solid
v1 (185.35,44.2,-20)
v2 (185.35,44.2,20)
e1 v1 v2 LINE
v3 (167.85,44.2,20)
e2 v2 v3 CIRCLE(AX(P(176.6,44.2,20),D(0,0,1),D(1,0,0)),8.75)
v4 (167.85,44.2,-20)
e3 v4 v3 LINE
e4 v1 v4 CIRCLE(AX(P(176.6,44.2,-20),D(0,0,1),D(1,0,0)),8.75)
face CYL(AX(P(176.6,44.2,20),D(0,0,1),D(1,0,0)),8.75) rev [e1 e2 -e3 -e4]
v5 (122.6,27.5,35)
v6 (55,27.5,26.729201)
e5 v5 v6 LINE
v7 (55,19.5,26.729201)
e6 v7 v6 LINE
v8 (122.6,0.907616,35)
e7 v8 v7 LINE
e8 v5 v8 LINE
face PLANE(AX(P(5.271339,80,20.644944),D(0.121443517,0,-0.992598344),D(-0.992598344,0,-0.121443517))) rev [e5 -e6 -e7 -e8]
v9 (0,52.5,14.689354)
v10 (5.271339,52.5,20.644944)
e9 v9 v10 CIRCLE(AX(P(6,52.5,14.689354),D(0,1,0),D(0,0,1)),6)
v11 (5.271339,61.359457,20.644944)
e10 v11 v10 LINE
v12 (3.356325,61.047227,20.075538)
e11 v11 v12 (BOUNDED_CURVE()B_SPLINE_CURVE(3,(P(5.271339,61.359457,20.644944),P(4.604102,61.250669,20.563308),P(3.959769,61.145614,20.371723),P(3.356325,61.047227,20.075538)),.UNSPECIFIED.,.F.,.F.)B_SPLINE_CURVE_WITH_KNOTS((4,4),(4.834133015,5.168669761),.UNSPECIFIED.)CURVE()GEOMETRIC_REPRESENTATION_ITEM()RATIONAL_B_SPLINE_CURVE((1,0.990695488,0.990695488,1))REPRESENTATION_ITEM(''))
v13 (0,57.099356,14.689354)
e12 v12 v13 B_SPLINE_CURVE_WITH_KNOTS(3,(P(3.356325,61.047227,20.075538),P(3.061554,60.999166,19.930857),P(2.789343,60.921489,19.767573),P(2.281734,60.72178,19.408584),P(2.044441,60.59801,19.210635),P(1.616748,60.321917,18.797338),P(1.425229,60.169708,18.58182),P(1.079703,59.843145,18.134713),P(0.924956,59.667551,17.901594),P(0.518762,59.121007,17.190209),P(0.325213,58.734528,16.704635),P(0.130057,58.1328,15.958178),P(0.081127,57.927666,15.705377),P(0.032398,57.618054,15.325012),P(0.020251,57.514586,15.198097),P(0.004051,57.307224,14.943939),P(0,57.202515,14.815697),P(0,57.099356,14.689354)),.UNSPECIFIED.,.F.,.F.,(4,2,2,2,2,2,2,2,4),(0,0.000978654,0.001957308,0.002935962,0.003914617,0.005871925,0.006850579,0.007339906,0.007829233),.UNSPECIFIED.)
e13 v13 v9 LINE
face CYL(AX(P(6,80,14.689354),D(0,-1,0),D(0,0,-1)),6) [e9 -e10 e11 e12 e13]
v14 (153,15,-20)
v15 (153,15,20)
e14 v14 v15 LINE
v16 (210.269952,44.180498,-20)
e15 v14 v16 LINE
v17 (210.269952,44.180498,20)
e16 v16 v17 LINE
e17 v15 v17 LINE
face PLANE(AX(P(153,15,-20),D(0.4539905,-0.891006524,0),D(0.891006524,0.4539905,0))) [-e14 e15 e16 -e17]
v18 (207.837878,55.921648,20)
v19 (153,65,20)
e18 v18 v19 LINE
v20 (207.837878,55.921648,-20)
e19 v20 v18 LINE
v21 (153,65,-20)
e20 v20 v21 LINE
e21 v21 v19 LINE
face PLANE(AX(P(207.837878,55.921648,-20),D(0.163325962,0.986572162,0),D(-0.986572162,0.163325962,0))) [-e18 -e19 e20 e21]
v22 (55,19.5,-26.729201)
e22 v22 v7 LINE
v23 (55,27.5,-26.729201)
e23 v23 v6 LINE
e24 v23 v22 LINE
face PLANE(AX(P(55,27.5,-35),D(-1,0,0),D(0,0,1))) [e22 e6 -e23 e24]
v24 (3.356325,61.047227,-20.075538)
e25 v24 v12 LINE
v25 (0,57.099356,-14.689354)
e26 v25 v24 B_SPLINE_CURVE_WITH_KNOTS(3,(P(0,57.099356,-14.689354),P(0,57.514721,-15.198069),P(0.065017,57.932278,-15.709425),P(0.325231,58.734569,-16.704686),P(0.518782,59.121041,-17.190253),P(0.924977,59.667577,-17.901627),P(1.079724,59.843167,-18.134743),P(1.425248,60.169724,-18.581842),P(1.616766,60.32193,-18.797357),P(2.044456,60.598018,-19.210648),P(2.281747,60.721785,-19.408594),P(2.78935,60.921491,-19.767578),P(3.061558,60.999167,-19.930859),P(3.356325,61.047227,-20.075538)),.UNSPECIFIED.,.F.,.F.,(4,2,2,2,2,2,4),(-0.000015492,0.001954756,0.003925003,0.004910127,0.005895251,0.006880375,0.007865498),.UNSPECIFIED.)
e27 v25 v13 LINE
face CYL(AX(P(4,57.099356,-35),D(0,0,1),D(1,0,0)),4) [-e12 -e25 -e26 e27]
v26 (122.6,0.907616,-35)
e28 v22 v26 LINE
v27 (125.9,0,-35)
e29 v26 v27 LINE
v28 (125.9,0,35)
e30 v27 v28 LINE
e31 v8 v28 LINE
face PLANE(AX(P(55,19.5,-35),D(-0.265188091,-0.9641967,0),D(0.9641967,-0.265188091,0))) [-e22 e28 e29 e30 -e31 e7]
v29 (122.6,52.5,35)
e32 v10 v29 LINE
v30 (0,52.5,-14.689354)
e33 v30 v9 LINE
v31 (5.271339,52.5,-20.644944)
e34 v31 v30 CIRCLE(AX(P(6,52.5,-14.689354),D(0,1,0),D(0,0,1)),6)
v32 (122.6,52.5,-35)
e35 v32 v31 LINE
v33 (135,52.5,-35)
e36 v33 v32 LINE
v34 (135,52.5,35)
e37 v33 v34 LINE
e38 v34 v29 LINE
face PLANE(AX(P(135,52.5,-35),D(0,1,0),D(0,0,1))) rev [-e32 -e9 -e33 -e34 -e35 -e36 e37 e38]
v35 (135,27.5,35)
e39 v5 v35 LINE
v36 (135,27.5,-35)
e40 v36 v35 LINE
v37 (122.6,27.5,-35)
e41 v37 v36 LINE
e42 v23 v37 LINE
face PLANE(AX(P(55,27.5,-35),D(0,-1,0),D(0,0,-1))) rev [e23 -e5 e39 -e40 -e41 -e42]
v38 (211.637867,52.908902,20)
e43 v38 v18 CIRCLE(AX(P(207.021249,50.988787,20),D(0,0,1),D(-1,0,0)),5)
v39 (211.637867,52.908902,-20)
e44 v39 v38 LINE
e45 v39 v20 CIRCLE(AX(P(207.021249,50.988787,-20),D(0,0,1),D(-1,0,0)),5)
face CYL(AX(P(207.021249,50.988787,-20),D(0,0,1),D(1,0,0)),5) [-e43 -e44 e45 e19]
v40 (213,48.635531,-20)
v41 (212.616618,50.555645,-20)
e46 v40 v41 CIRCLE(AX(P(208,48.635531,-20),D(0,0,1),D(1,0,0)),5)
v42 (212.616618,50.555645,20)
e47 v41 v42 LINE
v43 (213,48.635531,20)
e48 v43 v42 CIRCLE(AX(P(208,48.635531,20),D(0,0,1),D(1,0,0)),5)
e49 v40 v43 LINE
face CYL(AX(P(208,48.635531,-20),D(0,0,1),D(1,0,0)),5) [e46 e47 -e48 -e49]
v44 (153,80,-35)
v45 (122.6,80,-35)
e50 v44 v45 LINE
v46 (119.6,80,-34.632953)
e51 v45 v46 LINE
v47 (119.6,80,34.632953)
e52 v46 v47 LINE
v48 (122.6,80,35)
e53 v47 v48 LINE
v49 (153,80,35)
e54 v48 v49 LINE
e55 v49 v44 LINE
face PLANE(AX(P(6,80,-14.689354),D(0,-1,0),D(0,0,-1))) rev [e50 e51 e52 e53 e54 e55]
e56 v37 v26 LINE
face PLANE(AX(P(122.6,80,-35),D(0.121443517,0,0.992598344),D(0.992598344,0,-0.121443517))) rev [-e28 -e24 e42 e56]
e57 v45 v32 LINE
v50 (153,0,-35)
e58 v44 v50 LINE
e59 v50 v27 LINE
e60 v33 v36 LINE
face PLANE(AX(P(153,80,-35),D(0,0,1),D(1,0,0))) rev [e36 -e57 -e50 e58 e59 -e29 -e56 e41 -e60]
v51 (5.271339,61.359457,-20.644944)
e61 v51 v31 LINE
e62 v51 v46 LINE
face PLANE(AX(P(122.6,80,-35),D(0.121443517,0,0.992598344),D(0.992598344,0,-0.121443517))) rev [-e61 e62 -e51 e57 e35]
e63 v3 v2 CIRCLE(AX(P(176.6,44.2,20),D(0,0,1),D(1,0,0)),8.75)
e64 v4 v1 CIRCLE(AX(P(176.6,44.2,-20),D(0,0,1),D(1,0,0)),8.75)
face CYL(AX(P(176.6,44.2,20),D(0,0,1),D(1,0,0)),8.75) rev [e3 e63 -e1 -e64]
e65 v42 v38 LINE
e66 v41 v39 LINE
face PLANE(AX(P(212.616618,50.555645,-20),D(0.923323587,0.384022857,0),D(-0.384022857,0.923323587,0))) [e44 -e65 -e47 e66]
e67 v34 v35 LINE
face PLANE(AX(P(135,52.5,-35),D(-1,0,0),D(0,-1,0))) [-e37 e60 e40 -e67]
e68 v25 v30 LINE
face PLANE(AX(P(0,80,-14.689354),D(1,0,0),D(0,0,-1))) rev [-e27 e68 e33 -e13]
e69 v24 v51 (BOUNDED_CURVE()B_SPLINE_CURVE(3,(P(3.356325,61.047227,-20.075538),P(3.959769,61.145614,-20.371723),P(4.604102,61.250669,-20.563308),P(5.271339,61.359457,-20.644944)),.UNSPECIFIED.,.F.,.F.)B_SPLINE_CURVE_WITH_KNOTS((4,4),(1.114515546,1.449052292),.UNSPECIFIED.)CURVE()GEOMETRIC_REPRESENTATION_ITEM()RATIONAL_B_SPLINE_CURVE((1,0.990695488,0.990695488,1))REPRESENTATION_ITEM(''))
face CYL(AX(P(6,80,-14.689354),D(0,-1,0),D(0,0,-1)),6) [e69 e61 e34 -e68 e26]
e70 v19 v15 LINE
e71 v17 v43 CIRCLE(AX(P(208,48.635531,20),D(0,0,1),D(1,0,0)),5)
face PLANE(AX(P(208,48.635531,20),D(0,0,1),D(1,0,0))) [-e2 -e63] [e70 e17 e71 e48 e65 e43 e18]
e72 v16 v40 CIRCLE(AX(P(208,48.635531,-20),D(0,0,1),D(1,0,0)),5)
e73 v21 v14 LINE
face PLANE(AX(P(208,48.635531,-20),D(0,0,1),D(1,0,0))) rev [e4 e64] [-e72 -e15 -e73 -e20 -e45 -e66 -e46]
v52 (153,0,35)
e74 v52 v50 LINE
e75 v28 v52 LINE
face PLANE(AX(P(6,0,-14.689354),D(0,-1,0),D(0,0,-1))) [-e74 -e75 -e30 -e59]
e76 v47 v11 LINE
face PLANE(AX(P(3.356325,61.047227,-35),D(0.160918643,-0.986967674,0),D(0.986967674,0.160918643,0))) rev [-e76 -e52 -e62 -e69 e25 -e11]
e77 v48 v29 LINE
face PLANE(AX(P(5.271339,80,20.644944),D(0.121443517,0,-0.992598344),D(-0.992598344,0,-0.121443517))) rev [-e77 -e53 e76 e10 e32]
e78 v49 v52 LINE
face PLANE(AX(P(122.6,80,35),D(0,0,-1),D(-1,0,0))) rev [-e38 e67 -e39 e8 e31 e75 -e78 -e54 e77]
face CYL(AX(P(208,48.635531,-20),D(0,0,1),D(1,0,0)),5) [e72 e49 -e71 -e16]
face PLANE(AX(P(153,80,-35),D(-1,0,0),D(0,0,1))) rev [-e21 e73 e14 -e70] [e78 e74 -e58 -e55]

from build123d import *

# Parameters (mm, degrees)
BOSS_EXTRUDE1_DEPTH      = 80
CUT_EXTRUDE1_DEPTH       = 177.164695669
CUT_EXTRUDE1_DEPTH_BACK  = 177.164695669
SKETCH2_OUTSIDE_W        = 192.26
SKETCH2_OUTSIDE_H        = 119.26
BOSS_EXTRUDE2_DEPTH      = 20
BOSS_EXTRUDE2_DEPTH_BACK = 20
M20_TAPPED_HOLE1_D       = 17.5


with BuildPart() as part:
    # Sketch1 → Boss-Extrude1 (new body)
    with BuildSketch(Plane(origin=(0, 0, 0), x_dir=(1, 0, 0), z_dir=(0, 1, 0))):
        with BuildLine():
            Line((0, 14.689353522), (0, -14.689353522))
            ThreePointArc((0, -14.689353522), (1.507118597, -18.666037655), (5.271338899, -20.644943585))
            Line((5.271338899, -20.644943585), (122.6, -35))
            Line((122.6, -35), (153, -35))
            Line((153, -35), (153, 35))
            Line((153, 35), (122.6, 35))
            Line((122.6, 35), (5.271338899, 20.644943585))
            ThreePointArc((5.271338899, 20.644943585), (1.507118597, 18.666037655), (0, 14.689353522))
        make_face()
    extrude(amount=BOSS_EXTRUDE1_DEPTH)

    # Sketch2 outside → Cut-Extrude1 (cut, two sides: drawn at the far end of the back side and taken through both)
    with BuildSketch(Plane.XY.offset(-CUT_EXTRUDE1_DEPTH_BACK)):
        with Locations((76.5, 40)):
            Rectangle(SKETCH2_OUTSIDE_W, SKETCH2_OUTSIDE_H)
        with BuildLine():
            Line((153, 80), (153, 0))
            Line((153, 0), (125.9, 0))
            Line((125.9, 0), (55, 19.5))
            Line((55, 19.5), (55, 27.5))
            Line((55, 27.5), (135, 27.5))
            Line((135, 27.5), (135, 52.5))
            Line((135, 52.5), (0, 52.5))
            Line((0, 52.5), (0, 57.099356274))
            ThreePointArc((0, 57.099356274), (0.95248476, 59.69023467), (3.35632543, 61.047226972))
            Line((3.35632543, 61.047226972), (119.6, 80))
            Line((119.6, 80), (153, 80))
        make_face(mode=Mode.SUBTRACT)
    extrude(amount=CUT_EXTRUDE1_DEPTH + CUT_EXTRUDE1_DEPTH_BACK, mode=Mode.SUBTRACT)

    # Sketch3 → Boss-Extrude2 (add, two sides: drawn at the far end of the back side and taken through both)
    with BuildSketch(Plane.XY.offset(-BOSS_EXTRUDE2_DEPTH_BACK)):
        with BuildLine():
            Line((153, 65), (153, 15))
            Line((153, 15), (210.269952499, 44.180498289))
            ThreePointArc((210.269952499, 44.180498289), (212.69221031, 46.908347535), (212.616617933, 50.555645193))
            Line((212.616617933, 50.555645193), (211.637866551, 52.908901571))
            ThreePointArc((211.637866551, 52.908901571), (210.127565677, 54.906796263), (207.837878429, 55.921648096))
            Line((207.837878429, 55.921648096), (153, 65))
        make_face()
    extrude(amount=BOSS_EXTRUDE2_DEPTH + BOSS_EXTRUDE2_DEPTH_BACK)

    # M20 Tapped Hole1 (through all)
    with Locations(Plane.XY.offset(20)):
        with Locations((176.6, 44.2)):
            Hole(M20_TAPPED_HOLE1_D / 2)


solid = part.part
